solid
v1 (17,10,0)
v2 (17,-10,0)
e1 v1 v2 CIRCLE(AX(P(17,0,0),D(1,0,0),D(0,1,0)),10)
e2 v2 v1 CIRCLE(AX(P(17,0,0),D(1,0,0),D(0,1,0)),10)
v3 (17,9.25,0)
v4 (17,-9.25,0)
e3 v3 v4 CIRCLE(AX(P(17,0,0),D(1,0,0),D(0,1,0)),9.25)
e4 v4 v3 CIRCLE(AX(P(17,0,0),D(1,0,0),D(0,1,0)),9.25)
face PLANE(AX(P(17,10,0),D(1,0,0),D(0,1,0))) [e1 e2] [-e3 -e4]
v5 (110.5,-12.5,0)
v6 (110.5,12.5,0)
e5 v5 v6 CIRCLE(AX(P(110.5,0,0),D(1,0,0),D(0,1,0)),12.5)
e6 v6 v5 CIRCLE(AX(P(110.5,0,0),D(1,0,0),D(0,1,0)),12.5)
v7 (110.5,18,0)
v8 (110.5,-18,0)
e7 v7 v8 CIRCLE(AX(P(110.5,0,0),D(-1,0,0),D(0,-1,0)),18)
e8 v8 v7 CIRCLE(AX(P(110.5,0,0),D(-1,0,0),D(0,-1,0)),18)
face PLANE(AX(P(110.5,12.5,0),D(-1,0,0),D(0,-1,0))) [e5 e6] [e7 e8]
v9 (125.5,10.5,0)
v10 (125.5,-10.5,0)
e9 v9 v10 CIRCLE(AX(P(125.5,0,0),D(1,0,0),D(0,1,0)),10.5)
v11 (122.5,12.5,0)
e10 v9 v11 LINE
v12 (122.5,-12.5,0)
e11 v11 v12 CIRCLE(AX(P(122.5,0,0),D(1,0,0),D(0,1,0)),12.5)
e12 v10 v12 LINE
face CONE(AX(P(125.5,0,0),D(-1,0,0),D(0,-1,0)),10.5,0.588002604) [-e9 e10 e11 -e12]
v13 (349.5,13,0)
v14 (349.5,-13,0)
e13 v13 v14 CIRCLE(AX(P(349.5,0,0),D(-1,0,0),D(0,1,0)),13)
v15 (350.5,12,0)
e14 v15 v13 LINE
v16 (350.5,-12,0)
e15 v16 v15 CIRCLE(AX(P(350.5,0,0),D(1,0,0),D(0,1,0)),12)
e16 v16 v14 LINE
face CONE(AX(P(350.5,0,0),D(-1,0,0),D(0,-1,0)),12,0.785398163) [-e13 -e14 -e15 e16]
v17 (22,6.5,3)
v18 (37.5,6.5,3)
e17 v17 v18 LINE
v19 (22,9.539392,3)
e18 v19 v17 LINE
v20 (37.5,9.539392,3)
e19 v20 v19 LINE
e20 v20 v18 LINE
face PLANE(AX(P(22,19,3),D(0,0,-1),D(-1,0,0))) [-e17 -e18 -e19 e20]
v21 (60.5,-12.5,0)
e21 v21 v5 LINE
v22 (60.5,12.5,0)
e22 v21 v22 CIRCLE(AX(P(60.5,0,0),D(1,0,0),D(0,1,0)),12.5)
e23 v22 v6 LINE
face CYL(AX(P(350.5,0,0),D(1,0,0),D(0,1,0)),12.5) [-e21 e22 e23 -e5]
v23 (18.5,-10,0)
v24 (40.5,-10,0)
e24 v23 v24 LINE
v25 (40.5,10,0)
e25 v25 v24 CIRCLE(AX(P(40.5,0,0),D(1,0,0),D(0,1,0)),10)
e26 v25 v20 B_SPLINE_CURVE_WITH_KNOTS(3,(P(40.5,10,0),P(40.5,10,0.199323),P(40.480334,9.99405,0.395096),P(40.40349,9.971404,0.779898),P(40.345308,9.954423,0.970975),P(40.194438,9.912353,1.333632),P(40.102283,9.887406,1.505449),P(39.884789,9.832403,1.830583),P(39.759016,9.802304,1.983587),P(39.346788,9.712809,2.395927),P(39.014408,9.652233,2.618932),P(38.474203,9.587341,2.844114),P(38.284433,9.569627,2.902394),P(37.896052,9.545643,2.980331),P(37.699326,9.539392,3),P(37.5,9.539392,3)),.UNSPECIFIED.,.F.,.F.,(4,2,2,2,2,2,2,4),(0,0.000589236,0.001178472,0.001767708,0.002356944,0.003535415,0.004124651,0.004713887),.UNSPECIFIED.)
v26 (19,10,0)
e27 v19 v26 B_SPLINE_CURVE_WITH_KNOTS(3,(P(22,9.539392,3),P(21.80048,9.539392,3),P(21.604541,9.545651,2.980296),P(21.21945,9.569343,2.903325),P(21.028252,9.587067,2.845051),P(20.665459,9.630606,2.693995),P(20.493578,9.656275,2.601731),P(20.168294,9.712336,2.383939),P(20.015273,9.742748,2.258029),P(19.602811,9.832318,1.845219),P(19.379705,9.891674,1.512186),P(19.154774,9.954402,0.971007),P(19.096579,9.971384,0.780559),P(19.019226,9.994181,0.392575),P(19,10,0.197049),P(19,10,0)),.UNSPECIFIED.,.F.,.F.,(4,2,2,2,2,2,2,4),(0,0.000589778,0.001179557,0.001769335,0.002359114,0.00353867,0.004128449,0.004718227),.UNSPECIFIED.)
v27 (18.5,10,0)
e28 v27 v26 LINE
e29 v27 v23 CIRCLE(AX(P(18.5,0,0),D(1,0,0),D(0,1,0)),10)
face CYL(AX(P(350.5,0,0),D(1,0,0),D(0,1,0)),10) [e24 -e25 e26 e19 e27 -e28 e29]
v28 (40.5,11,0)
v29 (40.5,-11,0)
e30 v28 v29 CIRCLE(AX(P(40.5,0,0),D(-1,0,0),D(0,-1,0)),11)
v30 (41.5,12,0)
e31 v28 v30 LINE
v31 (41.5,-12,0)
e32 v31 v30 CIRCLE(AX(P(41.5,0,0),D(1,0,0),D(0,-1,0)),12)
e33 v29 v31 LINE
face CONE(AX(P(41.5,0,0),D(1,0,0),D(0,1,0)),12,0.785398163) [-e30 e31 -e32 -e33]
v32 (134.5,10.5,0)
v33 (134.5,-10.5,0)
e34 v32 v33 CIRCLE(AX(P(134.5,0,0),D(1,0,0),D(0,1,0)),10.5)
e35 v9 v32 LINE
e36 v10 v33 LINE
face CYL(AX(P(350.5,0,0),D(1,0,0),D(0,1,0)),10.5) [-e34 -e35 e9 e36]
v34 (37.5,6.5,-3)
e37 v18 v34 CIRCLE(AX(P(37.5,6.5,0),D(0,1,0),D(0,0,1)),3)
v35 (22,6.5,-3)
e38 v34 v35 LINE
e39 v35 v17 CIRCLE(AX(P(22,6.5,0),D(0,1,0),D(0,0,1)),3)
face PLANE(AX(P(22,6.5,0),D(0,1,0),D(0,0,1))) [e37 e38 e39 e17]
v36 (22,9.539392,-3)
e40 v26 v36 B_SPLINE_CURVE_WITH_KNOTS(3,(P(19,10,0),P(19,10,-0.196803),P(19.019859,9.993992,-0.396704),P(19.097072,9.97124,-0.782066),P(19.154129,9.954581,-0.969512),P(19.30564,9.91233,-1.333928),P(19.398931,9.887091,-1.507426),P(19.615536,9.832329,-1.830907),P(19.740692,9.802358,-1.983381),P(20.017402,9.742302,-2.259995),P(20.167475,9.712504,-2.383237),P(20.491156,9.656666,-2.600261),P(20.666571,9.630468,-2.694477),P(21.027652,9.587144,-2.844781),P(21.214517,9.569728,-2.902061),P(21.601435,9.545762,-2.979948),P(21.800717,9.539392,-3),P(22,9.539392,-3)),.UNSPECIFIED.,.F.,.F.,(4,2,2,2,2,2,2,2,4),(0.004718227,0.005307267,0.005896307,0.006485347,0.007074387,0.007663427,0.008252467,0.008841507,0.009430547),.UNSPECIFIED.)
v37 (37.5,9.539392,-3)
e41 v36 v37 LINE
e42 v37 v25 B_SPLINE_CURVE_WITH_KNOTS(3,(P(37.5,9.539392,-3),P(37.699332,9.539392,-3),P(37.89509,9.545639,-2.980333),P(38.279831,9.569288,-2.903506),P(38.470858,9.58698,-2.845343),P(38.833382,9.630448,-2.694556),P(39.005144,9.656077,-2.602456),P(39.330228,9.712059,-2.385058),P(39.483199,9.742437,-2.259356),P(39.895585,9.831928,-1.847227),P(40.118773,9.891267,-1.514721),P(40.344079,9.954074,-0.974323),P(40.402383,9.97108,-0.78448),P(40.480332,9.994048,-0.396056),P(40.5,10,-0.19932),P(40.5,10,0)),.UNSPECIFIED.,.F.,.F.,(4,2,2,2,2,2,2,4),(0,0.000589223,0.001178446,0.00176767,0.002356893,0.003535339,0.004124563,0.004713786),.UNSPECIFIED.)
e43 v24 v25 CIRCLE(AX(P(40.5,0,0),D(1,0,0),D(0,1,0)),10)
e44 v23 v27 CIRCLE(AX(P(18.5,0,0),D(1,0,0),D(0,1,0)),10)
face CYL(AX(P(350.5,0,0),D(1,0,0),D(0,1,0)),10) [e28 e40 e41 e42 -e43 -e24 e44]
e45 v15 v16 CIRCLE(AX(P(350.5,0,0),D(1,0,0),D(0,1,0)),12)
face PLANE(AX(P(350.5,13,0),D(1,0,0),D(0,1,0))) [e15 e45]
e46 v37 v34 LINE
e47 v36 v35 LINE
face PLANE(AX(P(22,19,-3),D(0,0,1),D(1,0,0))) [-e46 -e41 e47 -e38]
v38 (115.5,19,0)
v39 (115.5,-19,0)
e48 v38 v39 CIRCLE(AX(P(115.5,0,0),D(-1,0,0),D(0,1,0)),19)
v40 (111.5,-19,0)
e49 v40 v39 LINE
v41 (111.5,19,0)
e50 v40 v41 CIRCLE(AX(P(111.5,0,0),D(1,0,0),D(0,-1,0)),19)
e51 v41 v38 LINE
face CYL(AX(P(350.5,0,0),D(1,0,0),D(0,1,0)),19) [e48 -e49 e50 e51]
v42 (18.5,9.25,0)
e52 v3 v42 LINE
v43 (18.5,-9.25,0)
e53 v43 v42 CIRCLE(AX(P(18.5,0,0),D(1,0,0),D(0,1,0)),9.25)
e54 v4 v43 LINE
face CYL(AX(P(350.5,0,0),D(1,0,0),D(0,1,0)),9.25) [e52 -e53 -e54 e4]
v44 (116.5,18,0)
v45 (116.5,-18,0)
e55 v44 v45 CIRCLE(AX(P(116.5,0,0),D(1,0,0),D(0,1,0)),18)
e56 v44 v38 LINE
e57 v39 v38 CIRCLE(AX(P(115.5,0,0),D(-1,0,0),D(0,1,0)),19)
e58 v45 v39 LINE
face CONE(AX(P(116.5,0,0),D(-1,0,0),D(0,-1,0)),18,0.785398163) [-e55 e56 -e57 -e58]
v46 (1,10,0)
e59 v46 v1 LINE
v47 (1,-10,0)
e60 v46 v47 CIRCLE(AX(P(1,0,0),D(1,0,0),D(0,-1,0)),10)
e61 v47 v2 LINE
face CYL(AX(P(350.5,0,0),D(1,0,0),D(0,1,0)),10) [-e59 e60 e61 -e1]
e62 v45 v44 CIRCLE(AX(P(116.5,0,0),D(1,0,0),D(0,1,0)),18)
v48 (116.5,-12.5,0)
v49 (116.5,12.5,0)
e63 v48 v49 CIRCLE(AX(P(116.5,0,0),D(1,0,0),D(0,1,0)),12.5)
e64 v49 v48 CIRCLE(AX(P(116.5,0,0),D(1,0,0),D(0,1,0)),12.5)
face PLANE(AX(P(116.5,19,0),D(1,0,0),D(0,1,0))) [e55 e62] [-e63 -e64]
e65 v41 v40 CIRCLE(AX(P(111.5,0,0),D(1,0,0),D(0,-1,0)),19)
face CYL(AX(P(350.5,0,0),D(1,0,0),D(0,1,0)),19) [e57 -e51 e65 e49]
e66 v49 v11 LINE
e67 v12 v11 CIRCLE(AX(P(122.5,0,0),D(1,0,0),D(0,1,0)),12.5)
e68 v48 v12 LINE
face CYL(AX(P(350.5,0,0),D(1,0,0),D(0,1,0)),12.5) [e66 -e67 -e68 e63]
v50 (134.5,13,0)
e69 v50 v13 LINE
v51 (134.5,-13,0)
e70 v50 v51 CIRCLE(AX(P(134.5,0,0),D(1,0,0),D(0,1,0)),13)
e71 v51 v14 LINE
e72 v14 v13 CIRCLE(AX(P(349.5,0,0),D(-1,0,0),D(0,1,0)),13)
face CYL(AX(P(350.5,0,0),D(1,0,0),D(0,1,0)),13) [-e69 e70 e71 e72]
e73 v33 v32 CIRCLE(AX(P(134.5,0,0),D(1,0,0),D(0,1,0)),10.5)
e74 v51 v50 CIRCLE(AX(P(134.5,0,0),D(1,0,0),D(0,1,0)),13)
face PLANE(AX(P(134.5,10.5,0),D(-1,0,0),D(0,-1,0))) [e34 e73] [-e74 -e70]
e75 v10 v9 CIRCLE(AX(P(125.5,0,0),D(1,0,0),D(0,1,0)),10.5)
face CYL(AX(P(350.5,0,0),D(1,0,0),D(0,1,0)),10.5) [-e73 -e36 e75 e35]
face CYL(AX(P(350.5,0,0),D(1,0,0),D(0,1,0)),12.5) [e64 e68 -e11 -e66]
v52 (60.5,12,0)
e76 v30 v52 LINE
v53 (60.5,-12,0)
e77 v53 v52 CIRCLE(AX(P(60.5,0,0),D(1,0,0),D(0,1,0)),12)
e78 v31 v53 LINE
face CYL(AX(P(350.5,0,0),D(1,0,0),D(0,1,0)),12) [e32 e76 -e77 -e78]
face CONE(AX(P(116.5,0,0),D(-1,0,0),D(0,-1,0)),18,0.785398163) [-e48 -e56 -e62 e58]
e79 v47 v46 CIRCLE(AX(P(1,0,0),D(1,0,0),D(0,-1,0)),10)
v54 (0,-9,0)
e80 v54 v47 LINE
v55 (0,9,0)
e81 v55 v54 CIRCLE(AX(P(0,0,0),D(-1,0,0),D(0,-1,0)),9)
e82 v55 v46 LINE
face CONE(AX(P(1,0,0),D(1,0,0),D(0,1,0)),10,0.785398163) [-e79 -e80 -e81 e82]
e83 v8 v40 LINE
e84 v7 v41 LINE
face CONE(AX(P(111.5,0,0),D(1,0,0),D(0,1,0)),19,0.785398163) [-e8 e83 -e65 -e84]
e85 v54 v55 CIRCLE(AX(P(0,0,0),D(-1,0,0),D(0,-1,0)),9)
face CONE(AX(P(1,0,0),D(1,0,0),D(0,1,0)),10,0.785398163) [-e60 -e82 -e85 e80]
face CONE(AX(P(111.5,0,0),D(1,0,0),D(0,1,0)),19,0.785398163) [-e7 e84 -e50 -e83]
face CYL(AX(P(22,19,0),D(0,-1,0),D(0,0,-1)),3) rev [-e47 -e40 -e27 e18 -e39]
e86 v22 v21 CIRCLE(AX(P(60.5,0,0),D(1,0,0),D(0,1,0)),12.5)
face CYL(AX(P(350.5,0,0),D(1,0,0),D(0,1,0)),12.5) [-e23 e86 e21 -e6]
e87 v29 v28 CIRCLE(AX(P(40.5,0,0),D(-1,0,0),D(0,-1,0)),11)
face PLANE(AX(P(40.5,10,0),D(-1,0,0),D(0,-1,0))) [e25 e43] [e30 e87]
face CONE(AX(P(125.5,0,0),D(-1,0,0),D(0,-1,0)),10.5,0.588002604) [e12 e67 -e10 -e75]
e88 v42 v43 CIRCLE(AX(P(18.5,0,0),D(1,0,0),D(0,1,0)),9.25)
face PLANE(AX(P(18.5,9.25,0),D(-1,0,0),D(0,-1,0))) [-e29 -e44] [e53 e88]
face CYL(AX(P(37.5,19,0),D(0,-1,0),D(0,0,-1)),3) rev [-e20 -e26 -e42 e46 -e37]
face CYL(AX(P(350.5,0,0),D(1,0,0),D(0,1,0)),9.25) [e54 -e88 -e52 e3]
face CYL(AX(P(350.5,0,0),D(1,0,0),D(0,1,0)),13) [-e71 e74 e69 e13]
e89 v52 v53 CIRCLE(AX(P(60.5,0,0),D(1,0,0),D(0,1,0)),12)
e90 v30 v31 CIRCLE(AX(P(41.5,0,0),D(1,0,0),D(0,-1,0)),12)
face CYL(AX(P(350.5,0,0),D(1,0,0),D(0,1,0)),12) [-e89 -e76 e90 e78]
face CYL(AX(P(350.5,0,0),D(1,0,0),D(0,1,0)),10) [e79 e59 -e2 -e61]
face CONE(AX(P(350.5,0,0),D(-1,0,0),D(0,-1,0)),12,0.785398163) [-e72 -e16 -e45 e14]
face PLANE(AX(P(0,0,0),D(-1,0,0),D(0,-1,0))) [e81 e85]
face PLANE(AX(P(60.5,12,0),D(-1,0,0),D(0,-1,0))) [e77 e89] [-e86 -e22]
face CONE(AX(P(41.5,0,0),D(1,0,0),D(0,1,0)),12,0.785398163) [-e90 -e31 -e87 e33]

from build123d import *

# Parameters (mm, degrees)
CUT_EXTRUDE_3_DEPTH = 352.939625504
CHAMFER_1_SIZE      = 1


with BuildPart() as part:
    # 草图1 → 旋转1 (revolve)
    with BuildSketch(Plane.XY):
        Polygon((0, 0), (0, 10), (17, 10), (17, 9.25), (18.5, 9.25), (18.5, 10), (40.5, 10), (40.5, 12), (60.5, 12), (60.5, 12.5), (110.5, 12.5), (110.5, 19), (116.5, 19), (116.5, 12.5), (122.5, 12.5), (125.5, 10.5), (134.5, 10.5), (134.5, 13), (350.5, 13), (350.5, 0), align=None)
    revolve(axis=Axis((350.5, 0, 0), (-1, 0, 0)))

    # 草图2 → 切除-拉伸3 (cut, through all)
    with BuildSketch(Plane(origin=(0, 6.5, 0), x_dir=(1, 0, 0), z_dir=(0, 1, 0))):
        with BuildLine():
            Line((22, 3), (37.5, 3))
            ThreePointArc((37.5, 3), (40.5, 0), (37.5, -3))
            Line((37.5, -3), (22, -3))
            ThreePointArc((22, -3), (19, 0), (22, 3))
        make_face()
    extrude(amount=CUT_EXTRUDE_3_DEPTH, mode=Mode.SUBTRACT)

    # 倒角1
    chamfer_1_edges = [part.edges().sort_by_distance(p)[0] for p in [
        (350.5, -13, 0),
        (116.5, -19, 0),
        (110.5, -19, 0),
        (40.5, -12, 0),
        (0, -10, 0),
    ]]
    chamfer(chamfer_1_edges, length=CHAMFER_1_SIZE)


solid = part.part
